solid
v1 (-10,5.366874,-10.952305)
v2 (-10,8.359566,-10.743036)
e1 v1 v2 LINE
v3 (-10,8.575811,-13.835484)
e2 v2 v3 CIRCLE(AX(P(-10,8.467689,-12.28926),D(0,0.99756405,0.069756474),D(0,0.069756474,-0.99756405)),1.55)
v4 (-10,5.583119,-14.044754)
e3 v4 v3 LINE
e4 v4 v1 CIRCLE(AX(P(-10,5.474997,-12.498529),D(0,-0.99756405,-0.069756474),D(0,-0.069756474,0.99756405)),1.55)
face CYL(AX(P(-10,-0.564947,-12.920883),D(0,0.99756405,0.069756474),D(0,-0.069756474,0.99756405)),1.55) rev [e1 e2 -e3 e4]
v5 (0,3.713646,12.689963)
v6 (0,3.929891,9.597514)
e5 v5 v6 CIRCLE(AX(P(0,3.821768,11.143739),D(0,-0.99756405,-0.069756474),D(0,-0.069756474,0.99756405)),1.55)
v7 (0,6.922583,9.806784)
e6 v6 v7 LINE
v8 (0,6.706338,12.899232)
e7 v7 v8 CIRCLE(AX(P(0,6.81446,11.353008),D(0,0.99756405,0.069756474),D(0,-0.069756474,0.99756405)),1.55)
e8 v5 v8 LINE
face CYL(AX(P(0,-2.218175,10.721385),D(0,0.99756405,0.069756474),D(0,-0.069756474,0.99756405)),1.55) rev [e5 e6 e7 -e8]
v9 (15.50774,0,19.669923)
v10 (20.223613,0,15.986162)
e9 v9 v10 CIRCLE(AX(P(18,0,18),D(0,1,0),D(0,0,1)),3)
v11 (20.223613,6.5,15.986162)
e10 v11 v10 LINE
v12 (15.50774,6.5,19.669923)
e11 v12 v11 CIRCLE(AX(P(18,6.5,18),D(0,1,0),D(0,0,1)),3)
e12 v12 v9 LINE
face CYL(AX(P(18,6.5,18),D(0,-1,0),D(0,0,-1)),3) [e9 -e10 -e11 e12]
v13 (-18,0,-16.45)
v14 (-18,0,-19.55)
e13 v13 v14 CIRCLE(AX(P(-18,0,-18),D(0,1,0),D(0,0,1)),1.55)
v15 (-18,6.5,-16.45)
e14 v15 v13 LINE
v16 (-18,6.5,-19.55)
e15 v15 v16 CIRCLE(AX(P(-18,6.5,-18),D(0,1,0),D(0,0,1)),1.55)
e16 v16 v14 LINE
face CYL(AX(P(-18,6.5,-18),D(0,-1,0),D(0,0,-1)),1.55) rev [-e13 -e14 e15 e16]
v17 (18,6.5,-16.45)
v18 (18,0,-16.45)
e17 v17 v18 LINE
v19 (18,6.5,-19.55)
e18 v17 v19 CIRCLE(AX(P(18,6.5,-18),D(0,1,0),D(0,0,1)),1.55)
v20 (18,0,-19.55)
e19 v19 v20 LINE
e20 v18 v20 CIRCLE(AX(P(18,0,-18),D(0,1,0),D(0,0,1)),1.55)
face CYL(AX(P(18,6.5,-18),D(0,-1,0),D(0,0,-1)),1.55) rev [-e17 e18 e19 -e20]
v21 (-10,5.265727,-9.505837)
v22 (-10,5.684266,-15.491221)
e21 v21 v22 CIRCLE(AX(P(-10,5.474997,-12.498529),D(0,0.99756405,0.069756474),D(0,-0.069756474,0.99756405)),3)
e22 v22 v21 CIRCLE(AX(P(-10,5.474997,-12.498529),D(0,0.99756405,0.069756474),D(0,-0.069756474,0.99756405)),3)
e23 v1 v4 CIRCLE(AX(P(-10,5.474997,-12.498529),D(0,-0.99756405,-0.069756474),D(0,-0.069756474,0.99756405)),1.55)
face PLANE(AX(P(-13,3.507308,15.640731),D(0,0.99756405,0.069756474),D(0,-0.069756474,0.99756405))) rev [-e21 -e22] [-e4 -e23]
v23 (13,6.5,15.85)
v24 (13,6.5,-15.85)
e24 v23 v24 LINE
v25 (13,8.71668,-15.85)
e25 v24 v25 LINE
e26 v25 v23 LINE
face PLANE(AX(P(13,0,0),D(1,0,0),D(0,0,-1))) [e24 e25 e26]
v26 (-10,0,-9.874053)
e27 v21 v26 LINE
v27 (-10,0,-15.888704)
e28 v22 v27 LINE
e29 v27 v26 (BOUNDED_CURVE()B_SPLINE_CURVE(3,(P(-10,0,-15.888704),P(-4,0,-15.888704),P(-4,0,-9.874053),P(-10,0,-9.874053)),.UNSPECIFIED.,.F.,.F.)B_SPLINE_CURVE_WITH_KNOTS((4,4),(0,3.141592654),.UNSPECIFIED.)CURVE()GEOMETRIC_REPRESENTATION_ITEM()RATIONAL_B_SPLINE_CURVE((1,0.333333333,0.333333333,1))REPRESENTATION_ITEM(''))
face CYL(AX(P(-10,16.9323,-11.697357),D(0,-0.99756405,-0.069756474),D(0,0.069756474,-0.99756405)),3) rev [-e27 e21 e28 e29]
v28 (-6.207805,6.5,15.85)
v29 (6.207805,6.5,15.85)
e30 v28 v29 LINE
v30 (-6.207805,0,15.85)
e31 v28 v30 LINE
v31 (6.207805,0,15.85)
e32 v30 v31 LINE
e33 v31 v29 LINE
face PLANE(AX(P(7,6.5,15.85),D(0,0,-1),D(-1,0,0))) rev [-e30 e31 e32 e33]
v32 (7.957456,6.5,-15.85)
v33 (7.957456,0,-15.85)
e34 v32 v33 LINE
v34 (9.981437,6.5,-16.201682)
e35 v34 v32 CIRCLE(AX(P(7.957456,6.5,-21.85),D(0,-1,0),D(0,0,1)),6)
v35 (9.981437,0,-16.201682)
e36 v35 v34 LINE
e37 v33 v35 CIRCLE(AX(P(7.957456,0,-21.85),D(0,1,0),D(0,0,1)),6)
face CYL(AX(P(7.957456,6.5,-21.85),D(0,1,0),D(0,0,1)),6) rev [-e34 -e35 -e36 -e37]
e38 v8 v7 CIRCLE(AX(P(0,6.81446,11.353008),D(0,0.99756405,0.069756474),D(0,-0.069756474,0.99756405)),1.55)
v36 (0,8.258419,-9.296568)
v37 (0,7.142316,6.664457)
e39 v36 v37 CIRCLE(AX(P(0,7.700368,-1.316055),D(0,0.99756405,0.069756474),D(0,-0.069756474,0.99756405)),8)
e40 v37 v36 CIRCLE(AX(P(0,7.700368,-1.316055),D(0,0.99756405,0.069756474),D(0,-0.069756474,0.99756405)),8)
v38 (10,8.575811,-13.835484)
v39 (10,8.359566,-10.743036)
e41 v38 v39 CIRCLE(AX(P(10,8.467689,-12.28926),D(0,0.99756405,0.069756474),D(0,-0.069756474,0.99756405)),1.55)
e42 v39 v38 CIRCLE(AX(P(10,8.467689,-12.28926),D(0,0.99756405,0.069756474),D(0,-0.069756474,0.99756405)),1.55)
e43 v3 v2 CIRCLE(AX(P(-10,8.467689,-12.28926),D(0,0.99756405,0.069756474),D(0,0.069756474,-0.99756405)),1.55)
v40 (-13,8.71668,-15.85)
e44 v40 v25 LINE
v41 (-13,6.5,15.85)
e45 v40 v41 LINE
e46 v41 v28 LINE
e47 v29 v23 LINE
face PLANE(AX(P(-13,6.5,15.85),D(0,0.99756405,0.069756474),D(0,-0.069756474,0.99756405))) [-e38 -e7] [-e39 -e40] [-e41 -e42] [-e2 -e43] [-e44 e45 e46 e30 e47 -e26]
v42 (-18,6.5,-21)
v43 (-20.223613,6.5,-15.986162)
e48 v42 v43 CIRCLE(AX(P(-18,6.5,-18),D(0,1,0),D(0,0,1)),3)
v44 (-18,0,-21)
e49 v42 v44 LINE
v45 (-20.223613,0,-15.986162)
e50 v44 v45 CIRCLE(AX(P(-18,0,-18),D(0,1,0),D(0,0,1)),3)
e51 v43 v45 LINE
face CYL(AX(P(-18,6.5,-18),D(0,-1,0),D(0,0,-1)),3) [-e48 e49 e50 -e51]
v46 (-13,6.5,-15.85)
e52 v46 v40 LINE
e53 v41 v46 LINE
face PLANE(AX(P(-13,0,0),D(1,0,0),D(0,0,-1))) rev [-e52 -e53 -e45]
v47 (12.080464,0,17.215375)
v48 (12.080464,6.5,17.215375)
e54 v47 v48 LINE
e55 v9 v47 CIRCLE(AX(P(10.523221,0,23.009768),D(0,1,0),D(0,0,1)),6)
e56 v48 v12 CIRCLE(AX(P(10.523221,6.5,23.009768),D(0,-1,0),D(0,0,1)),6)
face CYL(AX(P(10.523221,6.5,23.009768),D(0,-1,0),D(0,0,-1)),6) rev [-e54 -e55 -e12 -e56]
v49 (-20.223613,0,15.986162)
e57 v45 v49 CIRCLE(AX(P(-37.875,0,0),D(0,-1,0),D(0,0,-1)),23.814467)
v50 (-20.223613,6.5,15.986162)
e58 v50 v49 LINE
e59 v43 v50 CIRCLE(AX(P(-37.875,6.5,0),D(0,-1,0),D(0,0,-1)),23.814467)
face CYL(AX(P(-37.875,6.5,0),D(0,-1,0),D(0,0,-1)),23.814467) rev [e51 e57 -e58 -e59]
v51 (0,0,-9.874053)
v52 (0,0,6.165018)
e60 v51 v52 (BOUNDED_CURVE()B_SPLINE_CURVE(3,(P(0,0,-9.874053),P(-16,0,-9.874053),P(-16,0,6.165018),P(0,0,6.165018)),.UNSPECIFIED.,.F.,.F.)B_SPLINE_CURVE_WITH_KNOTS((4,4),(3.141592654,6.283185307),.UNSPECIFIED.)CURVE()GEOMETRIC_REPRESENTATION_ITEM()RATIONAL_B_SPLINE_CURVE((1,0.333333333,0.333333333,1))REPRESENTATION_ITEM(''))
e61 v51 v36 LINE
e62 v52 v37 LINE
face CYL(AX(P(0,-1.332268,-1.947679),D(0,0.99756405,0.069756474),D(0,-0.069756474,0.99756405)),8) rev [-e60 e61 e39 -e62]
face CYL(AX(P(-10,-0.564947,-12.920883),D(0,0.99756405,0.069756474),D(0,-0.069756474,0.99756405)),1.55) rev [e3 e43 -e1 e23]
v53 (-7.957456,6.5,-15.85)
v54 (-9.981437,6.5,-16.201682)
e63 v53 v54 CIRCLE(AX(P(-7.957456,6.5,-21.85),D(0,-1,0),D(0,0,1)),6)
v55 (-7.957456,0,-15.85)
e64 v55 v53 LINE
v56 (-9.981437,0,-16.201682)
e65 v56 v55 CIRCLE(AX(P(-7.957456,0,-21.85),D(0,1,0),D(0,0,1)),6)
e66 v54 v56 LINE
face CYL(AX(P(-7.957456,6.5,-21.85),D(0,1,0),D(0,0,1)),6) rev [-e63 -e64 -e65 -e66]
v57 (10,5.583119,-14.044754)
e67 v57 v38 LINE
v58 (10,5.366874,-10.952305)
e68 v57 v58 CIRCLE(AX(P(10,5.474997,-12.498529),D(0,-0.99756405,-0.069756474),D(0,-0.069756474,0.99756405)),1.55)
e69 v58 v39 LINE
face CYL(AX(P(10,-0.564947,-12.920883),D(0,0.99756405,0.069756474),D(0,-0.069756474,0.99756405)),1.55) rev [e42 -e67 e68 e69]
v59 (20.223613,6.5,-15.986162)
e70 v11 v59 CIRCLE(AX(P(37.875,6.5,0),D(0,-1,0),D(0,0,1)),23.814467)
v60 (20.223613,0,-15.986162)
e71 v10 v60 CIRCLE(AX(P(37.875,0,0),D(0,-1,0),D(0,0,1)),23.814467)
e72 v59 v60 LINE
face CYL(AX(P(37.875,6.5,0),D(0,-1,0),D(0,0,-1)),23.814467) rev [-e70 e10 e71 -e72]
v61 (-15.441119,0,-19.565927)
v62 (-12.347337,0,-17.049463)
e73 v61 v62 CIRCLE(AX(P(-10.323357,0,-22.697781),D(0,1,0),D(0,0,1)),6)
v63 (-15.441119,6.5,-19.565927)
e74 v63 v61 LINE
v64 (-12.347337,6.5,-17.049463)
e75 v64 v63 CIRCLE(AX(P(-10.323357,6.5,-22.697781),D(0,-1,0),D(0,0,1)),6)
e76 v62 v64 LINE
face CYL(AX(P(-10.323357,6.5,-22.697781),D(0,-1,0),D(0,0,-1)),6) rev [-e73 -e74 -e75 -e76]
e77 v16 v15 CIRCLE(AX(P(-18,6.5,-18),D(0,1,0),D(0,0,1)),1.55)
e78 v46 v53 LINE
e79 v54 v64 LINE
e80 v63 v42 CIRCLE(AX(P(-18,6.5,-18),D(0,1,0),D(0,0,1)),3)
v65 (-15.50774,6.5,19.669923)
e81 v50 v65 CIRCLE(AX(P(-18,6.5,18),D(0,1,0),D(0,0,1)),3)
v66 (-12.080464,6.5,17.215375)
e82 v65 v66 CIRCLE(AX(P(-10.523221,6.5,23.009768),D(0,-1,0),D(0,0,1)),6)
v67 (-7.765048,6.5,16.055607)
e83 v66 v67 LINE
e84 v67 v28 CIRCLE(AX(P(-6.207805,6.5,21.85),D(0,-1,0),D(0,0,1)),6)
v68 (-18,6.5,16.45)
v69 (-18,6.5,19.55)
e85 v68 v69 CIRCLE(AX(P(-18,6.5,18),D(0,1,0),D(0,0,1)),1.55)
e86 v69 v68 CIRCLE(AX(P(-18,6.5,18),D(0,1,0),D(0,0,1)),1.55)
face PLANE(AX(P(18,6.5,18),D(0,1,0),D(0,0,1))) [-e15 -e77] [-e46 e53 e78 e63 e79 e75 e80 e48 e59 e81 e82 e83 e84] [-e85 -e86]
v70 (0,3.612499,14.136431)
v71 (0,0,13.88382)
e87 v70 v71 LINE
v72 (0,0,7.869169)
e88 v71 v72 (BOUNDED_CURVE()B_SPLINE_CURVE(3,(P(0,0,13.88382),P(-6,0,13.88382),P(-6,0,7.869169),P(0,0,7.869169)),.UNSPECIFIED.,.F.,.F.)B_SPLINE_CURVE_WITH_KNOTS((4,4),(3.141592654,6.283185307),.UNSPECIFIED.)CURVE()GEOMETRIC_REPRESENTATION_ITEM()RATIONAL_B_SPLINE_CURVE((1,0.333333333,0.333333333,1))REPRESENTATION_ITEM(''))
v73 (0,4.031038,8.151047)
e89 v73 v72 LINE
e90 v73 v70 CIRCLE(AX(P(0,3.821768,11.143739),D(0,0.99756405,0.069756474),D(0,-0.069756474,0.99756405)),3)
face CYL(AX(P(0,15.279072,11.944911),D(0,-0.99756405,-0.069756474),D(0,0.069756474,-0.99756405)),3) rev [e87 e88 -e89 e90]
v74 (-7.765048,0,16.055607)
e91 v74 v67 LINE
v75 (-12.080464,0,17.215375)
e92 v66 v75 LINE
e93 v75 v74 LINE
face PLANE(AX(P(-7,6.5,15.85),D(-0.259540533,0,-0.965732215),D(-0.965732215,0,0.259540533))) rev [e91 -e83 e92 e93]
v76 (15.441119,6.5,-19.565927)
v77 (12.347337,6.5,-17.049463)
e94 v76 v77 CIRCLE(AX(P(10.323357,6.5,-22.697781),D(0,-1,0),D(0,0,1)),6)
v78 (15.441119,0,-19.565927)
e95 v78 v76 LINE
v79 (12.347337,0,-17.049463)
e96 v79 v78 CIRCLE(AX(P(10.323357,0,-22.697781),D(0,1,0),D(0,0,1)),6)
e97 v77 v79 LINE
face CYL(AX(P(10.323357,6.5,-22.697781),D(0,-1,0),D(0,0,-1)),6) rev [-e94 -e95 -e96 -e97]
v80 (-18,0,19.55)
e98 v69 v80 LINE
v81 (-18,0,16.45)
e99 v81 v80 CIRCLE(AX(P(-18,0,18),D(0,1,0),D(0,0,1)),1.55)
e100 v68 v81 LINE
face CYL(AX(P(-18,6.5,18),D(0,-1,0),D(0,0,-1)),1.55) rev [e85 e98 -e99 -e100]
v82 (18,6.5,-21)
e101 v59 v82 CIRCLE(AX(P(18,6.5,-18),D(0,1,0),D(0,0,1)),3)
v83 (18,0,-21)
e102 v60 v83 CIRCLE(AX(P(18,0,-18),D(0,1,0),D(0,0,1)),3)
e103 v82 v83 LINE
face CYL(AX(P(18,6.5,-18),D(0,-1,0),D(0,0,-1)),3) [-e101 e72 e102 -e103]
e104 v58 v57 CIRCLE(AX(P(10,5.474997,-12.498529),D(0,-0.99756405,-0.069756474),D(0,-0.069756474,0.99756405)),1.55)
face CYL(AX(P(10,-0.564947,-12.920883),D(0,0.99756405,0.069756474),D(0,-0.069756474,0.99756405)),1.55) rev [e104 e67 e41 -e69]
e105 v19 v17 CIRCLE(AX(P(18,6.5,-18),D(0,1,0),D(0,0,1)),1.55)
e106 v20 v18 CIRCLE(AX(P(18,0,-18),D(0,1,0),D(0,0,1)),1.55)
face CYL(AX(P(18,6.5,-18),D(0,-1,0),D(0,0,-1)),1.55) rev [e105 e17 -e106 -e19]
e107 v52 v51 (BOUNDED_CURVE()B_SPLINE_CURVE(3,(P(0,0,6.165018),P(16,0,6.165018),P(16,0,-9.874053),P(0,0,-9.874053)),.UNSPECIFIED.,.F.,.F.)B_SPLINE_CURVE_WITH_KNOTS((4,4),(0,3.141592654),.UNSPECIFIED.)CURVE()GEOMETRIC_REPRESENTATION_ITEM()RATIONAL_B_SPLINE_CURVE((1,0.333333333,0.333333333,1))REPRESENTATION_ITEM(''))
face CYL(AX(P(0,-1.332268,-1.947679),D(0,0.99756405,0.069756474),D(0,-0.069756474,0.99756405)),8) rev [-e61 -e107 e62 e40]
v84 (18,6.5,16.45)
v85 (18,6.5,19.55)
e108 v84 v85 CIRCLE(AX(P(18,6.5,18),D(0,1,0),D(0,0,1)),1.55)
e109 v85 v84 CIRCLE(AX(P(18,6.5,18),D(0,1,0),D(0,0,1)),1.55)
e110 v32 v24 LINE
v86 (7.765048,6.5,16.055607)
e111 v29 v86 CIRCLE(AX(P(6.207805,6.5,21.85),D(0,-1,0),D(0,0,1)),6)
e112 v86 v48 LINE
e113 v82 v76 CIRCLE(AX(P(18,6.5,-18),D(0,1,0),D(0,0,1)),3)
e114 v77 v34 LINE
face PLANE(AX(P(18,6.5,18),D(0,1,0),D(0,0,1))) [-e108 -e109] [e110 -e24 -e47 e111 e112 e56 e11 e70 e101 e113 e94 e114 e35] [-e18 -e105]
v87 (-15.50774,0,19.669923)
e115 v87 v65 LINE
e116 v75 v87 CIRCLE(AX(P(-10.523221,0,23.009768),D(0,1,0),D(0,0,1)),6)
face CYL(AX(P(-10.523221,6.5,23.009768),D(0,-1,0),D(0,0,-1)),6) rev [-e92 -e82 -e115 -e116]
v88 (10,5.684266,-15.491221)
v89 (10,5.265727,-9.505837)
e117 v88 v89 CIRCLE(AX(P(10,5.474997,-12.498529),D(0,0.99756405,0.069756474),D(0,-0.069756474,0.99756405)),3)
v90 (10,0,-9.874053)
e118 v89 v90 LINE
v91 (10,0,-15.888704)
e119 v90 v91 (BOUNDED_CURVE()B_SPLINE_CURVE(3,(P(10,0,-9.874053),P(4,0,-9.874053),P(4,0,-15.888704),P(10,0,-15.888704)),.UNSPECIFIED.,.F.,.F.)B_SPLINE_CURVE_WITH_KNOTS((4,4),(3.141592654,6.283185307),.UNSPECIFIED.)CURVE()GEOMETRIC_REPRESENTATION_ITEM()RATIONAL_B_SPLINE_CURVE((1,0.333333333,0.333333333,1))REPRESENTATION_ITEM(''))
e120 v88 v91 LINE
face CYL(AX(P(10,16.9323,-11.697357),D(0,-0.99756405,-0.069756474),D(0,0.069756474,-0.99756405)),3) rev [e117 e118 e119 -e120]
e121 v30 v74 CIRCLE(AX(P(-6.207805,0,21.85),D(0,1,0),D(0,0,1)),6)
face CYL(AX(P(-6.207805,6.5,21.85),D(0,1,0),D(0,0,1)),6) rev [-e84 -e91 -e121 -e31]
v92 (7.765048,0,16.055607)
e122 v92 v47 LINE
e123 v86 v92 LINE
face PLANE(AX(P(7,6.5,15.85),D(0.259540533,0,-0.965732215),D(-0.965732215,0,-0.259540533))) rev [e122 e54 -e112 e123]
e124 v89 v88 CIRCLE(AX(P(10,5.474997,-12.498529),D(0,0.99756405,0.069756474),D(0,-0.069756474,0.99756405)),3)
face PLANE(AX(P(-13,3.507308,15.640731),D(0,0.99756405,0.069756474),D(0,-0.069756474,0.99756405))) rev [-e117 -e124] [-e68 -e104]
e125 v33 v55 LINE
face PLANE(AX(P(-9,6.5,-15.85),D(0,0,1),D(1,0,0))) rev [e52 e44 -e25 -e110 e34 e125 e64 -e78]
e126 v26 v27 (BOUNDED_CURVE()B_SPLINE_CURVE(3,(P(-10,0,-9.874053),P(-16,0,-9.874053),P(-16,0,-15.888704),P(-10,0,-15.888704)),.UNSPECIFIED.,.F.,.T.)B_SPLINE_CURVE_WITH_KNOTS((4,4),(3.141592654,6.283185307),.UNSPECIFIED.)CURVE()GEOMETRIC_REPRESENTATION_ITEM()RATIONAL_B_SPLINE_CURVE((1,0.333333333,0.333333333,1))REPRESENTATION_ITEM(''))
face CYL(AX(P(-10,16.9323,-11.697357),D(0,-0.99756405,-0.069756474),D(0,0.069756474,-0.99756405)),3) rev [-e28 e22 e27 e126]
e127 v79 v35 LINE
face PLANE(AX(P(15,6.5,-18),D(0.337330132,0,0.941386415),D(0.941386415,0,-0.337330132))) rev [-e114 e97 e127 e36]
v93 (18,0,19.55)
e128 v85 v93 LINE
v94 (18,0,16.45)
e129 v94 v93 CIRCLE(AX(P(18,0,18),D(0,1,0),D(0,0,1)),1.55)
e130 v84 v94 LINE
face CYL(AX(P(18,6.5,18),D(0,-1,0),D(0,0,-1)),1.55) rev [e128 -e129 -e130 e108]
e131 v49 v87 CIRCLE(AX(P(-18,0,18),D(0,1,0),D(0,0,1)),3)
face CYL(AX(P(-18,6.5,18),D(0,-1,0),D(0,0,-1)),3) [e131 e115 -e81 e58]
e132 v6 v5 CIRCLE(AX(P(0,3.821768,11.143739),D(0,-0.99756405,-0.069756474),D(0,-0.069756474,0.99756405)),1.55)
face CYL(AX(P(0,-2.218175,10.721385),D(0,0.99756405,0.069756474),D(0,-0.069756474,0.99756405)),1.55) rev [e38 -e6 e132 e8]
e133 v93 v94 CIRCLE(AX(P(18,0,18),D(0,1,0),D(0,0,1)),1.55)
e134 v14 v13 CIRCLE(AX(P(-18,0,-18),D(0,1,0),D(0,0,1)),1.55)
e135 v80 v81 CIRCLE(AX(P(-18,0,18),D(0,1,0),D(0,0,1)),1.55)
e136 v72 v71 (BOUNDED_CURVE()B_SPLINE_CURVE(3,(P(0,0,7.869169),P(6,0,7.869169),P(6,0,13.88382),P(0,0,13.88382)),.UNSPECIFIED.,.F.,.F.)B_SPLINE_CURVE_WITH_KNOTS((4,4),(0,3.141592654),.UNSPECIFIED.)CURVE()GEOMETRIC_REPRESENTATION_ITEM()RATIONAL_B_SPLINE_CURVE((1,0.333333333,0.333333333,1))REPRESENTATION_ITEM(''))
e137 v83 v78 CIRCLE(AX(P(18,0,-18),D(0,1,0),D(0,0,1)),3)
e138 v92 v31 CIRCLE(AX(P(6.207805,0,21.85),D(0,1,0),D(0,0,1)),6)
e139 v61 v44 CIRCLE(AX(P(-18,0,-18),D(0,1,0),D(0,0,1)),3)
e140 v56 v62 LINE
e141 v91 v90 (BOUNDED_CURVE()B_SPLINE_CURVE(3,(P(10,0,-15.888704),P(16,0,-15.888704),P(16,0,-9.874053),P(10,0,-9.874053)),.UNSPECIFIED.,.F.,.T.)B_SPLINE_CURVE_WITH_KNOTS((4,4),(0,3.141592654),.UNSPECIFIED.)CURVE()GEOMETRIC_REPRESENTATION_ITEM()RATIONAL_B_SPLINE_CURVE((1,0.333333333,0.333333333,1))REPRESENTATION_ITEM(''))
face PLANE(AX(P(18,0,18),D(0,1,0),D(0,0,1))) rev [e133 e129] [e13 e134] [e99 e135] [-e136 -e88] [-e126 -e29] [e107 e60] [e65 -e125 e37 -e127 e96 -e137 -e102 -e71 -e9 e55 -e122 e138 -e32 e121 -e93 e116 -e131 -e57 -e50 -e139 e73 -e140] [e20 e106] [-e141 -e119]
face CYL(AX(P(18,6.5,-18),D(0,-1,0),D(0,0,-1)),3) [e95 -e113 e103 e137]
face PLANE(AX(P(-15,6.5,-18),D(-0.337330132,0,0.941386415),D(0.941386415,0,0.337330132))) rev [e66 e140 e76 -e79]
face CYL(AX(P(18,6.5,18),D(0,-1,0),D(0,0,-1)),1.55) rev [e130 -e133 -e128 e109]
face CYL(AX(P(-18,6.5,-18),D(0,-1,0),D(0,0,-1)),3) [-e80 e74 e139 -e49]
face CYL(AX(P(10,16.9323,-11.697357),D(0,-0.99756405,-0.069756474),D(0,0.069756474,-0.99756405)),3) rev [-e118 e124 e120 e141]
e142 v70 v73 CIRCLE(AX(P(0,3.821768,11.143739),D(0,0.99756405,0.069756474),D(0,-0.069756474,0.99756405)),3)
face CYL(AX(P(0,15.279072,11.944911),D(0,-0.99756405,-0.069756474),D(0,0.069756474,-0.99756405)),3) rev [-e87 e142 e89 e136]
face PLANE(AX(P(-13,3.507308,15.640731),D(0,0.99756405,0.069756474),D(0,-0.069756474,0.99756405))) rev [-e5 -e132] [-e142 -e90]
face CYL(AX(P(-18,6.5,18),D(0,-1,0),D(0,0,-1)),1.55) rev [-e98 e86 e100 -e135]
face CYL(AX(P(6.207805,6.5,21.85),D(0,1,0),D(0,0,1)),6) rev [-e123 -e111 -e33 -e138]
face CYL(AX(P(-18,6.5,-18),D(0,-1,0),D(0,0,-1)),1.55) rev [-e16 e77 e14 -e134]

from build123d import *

# Parameters (mm, degrees)
SKETCH_1_R           = 1.55
EXTRUDE_1_DEPTH      = 6.5
EXTRUDE_2_DEPTH      = 13
EXTRUDE_2_DEPTH_BACK = 13
FILLET_1_R           = 6
SKETCH_5_R           = 1.55
SKETCH_5_R_2         = 8
CUT_EXTRUDE_3_DEPTH  = 32.013570632
SKETCH_6_R           = 3
CUT_EXTRUDE_10_DEPTH = 6


with BuildPart() as part:
    # 草图1 → 凸台-拉伸1 (new body)
    with BuildSketch(Plane(origin=(0, 0, 0), x_dir=(1, 0, 0), z_dir=(0, 1, 0))):
        with BuildLine():
            Line((-15, 18), (-9, 15.85))
            Line((-9, 15.85), (9, 15.85))
            Line((9, 15.85), (15, 18))
            ThreePointArc((15, 18), (19.079157226, 20.799181966), (20.223613121, 15.986161702))
            ThreePointArc((20.223613121, 15.986161702), (14.060533289, 0), (20.223613121, -15.986161702))
            ThreePointArc((20.223613121, -15.986161702), (19.079157226, -20.799181966), (15, -18))
            Line((15, -18), (7, -15.85))
            Line((7, -15.85), (-7, -15.85))
            Line((-7, -15.85), (-15, -18))
            ThreePointArc((-15, -18), (-19.079157226, -20.799181966), (-20.223613121, -15.986161702))
            ThreePointArc((-20.223613121, -15.986161702), (-14.060533289, 0), (-20.223613121, 15.986161702))
            ThreePointArc((-20.223613121, 15.986161702), (-19.079157226, 20.799181966), (-15, 18))
        make_face()
        with Locations(Location((18, 18, 0), (0, 0, 90))):
            Circle(SKETCH_1_R, mode=Mode.SUBTRACT)
        with Locations(Location((18, -18, 0), (0, 0, 90))):
            Circle(SKETCH_1_R, mode=Mode.SUBTRACT)
        with Locations(Location((-18, -18, 0), (0, 0, 90))):
            Circle(SKETCH_1_R, mode=Mode.SUBTRACT)
        with Locations(Location((-18, 18, 0), (0, 0, 90))):
            Circle(SKETCH_1_R, mode=Mode.SUBTRACT)
    extrude(amount=EXTRUDE_1_DEPTH)

    # 草图3 → 凸台-拉伸2 (add, two sides: drawn at the far end of the back side and taken through both)
    with BuildSketch(Plane(origin=(0, 0, 0), x_dir=(0, 0, -1), z_dir=(1, 0, 0)).offset(-EXTRUDE_2_DEPTH_BACK)):
        Polygon((-15.85, 6.5), (15.85, 6.5), (15.85, 8.716679939), align=None)
    extrude(amount=EXTRUDE_2_DEPTH + EXTRUDE_2_DEPTH_BACK)

    # 圆角1
    fillet_1_edges = [part.edges().sort_by_distance(p)[0] for p in [
        (15, 3.25, 18),
        (7, 3.25, 15.85),
        (-7, 3.25, 15.85),
        (-15, 3.25, 18),
        (-15, 3.25, -18),
        (-9, 3.25, -15.85),
        (9, 3.25, -15.85),
        (15, 3.25, -18),
    ]]
    fillet(fillet_1_edges, radius=FILLET_1_R)

    # 草图5 → 切除-拉伸3 (cut, through all)
    with BuildSketch(Plane(origin=(0, 7.571318049, 0.529438133), x_dir=(1, 0, 0), z_dir=(0, 0.9975640502598243, 0.06975647374412569))):
        with Locations(Location((10, 12.85, 0), (0, 0, 270))):
            Circle(SKETCH_5_R)
        with Locations(Location((0, -10.85, 0), (0, 0, 270))):
            Circle(SKETCH_5_R)
        with Locations(Location((-10, 12.85, 0), (0, 0, 270))):
            Circle(SKETCH_5_R)
        with Locations(Location((0, 1.85, 0), (0, 0, 270))):
            Circle(SKETCH_5_R_2)
    extrude(amount=-CUT_EXTRUDE_3_DEPTH, mode=Mode.SUBTRACT)

    # 草图6 → 切除-拉伸10 (cut)
    with BuildSketch(Plane(origin=(0, 1.528635135, -42.076453462), x_dir=(-1, 0, 0), z_dir=(0, 0.9975640502598243, 0.06975647374412568))):
        with Locations(Location((0, 52.930589533, 0), (0, 0, 270))):
            Circle(SKETCH_6_R)
        with Locations(Location((10, 29.230589533, 0), (0, 0, 270))):
            Circle(SKETCH_6_R)
        with Locations(Location((-10, 29.230589533, 0), (0, 0, 270))):
            Circle(SKETCH_6_R)
    extrude(amount=CUT_EXTRUDE_10_DEPTH, mode=Mode.SUBTRACT)


solid = part.part
